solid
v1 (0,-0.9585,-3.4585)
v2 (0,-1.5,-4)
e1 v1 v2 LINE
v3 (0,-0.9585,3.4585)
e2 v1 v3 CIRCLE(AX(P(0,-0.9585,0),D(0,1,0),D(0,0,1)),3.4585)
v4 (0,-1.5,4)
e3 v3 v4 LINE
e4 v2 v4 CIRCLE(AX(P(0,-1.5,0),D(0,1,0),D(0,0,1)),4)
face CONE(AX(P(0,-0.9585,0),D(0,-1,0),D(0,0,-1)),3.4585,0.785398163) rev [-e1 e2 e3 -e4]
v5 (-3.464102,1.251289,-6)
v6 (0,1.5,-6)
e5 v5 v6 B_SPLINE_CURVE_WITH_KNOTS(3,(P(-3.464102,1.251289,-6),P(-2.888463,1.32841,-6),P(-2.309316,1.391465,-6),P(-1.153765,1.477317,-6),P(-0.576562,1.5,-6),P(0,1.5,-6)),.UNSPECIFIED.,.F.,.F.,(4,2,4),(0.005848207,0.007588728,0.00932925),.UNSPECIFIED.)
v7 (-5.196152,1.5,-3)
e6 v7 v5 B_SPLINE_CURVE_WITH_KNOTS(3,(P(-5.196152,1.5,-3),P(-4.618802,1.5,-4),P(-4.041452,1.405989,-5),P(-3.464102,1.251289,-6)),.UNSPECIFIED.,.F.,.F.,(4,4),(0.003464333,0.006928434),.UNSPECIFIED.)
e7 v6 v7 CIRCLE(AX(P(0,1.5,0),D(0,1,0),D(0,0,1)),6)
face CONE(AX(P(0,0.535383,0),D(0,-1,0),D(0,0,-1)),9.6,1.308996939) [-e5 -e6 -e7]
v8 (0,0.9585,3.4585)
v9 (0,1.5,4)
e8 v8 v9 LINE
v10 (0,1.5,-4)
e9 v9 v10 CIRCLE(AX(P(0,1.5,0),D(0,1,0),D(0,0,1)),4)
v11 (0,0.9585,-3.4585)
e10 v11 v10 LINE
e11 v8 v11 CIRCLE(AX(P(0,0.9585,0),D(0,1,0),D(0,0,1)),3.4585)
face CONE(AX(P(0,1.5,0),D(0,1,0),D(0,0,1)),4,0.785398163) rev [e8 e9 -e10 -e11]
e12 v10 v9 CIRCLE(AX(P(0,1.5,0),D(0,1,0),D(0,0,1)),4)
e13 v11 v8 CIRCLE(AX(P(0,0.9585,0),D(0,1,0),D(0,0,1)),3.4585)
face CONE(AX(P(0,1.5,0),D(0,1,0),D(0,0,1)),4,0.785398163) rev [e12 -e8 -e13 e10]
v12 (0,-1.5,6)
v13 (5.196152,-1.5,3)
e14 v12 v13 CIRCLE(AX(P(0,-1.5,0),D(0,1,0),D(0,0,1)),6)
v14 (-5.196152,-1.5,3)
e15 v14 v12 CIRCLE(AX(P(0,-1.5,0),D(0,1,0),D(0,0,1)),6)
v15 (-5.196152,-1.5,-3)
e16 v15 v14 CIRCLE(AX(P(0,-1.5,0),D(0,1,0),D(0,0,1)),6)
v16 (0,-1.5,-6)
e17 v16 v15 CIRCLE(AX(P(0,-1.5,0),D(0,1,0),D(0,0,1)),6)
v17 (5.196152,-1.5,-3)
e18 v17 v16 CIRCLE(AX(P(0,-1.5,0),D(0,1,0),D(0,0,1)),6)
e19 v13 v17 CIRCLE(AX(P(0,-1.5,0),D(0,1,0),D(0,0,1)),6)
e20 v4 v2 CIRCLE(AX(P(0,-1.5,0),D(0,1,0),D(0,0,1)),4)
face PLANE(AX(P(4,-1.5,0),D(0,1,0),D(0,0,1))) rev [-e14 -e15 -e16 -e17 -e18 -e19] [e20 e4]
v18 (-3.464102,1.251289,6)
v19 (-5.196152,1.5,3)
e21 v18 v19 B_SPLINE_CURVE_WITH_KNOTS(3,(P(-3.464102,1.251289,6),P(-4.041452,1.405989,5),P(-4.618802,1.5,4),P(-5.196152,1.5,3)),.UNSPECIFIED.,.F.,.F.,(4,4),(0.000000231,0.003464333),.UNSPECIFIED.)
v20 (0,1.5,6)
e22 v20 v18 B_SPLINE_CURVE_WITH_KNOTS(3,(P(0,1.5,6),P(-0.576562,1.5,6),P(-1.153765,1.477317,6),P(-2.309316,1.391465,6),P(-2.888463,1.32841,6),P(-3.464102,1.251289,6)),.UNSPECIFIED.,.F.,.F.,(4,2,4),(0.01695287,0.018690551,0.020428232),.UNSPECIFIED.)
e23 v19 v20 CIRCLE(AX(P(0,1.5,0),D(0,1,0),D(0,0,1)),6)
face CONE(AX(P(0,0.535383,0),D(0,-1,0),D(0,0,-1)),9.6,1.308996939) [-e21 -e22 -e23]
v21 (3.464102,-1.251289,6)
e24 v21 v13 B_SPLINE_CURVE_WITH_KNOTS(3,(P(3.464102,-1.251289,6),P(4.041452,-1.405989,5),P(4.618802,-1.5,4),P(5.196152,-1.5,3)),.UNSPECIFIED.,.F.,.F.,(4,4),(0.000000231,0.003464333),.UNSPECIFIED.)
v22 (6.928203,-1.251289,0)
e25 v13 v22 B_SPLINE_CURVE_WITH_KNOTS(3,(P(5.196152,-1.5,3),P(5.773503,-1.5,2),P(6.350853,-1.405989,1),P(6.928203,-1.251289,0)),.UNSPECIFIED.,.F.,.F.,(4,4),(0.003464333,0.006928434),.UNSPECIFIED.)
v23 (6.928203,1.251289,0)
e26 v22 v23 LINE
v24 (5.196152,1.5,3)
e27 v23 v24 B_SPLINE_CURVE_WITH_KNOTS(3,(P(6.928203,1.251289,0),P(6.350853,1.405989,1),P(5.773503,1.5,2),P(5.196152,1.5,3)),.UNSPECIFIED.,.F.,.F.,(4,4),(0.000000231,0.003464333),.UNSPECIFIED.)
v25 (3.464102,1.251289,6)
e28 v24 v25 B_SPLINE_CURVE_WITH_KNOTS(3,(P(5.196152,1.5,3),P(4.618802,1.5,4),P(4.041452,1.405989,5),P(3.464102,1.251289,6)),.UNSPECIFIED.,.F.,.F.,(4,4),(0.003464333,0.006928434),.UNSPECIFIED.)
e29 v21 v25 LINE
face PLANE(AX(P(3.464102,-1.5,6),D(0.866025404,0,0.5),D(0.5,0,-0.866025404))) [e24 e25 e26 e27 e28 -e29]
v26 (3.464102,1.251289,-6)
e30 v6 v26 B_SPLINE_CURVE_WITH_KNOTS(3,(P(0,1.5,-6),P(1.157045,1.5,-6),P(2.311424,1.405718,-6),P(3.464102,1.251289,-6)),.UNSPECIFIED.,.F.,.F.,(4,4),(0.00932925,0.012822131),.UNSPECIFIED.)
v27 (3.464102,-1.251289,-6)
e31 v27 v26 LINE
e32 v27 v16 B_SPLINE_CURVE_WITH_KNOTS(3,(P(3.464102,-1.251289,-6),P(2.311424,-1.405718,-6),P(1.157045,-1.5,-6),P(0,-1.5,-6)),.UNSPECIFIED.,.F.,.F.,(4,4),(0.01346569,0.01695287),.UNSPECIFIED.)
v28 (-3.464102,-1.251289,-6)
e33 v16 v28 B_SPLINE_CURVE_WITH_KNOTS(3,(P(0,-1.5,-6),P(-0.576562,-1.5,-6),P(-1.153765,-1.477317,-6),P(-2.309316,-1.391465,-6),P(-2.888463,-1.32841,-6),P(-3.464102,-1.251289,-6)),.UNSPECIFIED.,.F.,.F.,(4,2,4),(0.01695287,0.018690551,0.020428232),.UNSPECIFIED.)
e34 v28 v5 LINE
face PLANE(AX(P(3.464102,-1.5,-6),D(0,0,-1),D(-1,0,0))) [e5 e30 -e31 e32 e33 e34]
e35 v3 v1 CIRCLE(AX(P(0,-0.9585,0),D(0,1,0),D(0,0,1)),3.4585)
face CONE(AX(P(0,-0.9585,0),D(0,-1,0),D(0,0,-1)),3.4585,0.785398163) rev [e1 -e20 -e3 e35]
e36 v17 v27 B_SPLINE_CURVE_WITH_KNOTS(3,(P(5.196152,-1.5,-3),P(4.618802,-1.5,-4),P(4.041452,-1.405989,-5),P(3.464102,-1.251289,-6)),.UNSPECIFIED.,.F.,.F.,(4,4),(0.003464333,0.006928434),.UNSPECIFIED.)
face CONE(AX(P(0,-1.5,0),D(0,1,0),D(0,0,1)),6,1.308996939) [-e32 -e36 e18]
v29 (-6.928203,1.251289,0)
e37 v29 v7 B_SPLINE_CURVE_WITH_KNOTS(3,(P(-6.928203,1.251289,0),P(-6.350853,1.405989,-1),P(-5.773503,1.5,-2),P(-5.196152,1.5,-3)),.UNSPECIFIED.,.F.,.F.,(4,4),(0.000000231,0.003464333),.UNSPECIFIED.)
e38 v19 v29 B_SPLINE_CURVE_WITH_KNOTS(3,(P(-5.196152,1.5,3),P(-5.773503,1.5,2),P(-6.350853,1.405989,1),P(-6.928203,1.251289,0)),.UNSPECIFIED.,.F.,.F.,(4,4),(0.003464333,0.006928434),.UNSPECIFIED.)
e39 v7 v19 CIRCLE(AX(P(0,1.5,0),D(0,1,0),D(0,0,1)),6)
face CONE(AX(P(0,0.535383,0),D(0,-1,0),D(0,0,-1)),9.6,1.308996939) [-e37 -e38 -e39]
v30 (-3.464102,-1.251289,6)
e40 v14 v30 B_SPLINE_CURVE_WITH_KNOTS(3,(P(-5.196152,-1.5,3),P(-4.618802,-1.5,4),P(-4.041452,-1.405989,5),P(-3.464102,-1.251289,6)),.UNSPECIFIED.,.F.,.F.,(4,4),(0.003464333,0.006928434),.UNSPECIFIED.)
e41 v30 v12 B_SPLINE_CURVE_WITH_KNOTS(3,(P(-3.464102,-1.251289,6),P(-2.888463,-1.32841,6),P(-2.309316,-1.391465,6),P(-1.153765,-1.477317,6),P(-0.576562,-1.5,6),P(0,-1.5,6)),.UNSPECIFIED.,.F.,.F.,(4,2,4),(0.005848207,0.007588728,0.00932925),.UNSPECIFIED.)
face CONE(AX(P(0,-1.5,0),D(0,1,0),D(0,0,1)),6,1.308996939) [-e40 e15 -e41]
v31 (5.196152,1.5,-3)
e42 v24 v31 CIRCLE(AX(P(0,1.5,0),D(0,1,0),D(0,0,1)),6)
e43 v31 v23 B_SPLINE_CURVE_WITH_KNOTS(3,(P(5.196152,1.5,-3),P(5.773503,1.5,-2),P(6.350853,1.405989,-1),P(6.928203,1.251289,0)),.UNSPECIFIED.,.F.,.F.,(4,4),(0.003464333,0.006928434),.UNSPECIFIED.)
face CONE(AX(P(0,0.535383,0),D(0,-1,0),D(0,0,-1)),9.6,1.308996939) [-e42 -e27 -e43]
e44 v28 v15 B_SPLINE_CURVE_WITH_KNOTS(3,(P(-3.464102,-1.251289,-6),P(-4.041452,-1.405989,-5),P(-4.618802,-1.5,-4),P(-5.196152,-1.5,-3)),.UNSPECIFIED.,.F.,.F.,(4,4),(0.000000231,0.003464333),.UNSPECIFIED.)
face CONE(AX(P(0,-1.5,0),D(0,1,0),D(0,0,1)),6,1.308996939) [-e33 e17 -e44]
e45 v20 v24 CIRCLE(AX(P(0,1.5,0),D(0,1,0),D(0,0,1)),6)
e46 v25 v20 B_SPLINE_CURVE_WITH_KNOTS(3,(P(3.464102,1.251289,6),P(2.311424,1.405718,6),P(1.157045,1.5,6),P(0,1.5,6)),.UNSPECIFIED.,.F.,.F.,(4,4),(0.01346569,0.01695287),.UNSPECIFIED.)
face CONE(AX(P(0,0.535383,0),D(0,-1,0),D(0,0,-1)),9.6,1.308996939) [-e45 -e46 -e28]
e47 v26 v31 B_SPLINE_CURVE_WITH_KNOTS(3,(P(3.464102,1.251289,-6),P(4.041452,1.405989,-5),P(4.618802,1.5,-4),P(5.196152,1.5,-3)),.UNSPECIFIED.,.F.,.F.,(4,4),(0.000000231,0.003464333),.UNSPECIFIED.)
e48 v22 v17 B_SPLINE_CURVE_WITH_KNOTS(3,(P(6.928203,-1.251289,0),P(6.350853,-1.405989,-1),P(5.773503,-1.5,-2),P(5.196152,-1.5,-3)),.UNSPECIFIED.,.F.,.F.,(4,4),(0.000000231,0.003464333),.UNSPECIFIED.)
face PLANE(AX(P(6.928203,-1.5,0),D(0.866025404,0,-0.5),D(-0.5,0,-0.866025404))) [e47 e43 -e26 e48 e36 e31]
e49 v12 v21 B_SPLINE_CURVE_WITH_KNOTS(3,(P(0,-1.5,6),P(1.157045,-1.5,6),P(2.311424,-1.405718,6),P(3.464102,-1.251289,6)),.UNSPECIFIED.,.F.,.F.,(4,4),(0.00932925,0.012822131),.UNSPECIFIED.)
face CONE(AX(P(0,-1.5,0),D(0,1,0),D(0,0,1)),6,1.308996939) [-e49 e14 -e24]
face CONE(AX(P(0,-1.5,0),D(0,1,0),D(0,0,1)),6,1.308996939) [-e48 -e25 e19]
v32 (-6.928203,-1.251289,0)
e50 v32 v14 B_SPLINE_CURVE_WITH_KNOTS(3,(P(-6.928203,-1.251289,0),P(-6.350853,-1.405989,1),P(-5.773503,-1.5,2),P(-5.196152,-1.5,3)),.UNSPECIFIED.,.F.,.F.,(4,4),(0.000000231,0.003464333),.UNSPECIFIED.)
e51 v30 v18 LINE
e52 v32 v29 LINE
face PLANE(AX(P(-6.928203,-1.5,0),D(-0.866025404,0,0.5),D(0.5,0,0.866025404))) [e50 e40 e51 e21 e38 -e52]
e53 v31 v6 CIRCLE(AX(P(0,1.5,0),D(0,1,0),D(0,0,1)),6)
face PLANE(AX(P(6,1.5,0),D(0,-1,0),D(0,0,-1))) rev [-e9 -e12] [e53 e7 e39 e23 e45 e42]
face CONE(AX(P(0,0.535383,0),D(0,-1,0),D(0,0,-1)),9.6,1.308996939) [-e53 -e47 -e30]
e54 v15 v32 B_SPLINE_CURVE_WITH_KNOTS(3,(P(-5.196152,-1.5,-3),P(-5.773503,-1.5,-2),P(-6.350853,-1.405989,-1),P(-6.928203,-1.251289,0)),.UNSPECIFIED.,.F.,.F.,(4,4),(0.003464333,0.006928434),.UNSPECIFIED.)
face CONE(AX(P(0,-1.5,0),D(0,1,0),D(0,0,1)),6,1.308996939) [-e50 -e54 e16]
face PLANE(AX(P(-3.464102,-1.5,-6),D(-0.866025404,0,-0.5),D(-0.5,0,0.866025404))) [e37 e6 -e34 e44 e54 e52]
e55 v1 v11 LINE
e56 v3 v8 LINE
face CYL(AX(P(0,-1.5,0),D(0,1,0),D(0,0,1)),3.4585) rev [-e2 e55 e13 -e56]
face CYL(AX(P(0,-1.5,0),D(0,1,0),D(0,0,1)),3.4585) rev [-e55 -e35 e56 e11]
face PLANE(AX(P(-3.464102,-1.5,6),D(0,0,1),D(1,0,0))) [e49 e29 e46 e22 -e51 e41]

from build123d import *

# Parameters (mm, degrees)
CUT_EXTRUDE_1_DEPTH      = 1.5
CUT_EXTRUDE_1_DEPTH_BACK = 1.5
SKETCH_2_R               = 12


with BuildPart() as part:
    # 草图1 → 旋转1 (revolve)
    with BuildSketch(Plane.XY, mode=Mode.PRIVATE) as revolve_1_sk:
        Polygon((3.4585, -0.9585), (4, -1.5), (6, -1.5), (9.6, -0.535382907), (9.6, 0.535382907), (6, 1.5), (4, 1.5), (3.4585, 0.9585), align=None)
    revolve(revolve_1_sk.sketch.rotate(Axis((0, -1.5, 0), (0, 1, 0)), 270), axis=Axis((0, -1.5, 0), (0, 1, 0)))

    # 草图2 → 切除-拉伸1 (cut, two sides: drawn at the far end of the back side and taken through both)
    with BuildSketch(Plane(origin=(0, 0, 0), x_dir=(1, 0, 0), z_dir=(0, 1, 0)).offset(-CUT_EXTRUDE_1_DEPTH_BACK)):
        Circle(SKETCH_2_R)
        Polygon((-6.92820323, 0), (-3.464101615, -6), (3.464101615, -6), (6.92820323, 0), (3.464101615, 6), (-3.464101615, 6), align=None, mode=Mode.SUBTRACT)
    extrude(amount=CUT_EXTRUDE_1_DEPTH + CUT_EXTRUDE_1_DEPTH_BACK, mode=Mode.SUBTRACT)


solid = part.part
